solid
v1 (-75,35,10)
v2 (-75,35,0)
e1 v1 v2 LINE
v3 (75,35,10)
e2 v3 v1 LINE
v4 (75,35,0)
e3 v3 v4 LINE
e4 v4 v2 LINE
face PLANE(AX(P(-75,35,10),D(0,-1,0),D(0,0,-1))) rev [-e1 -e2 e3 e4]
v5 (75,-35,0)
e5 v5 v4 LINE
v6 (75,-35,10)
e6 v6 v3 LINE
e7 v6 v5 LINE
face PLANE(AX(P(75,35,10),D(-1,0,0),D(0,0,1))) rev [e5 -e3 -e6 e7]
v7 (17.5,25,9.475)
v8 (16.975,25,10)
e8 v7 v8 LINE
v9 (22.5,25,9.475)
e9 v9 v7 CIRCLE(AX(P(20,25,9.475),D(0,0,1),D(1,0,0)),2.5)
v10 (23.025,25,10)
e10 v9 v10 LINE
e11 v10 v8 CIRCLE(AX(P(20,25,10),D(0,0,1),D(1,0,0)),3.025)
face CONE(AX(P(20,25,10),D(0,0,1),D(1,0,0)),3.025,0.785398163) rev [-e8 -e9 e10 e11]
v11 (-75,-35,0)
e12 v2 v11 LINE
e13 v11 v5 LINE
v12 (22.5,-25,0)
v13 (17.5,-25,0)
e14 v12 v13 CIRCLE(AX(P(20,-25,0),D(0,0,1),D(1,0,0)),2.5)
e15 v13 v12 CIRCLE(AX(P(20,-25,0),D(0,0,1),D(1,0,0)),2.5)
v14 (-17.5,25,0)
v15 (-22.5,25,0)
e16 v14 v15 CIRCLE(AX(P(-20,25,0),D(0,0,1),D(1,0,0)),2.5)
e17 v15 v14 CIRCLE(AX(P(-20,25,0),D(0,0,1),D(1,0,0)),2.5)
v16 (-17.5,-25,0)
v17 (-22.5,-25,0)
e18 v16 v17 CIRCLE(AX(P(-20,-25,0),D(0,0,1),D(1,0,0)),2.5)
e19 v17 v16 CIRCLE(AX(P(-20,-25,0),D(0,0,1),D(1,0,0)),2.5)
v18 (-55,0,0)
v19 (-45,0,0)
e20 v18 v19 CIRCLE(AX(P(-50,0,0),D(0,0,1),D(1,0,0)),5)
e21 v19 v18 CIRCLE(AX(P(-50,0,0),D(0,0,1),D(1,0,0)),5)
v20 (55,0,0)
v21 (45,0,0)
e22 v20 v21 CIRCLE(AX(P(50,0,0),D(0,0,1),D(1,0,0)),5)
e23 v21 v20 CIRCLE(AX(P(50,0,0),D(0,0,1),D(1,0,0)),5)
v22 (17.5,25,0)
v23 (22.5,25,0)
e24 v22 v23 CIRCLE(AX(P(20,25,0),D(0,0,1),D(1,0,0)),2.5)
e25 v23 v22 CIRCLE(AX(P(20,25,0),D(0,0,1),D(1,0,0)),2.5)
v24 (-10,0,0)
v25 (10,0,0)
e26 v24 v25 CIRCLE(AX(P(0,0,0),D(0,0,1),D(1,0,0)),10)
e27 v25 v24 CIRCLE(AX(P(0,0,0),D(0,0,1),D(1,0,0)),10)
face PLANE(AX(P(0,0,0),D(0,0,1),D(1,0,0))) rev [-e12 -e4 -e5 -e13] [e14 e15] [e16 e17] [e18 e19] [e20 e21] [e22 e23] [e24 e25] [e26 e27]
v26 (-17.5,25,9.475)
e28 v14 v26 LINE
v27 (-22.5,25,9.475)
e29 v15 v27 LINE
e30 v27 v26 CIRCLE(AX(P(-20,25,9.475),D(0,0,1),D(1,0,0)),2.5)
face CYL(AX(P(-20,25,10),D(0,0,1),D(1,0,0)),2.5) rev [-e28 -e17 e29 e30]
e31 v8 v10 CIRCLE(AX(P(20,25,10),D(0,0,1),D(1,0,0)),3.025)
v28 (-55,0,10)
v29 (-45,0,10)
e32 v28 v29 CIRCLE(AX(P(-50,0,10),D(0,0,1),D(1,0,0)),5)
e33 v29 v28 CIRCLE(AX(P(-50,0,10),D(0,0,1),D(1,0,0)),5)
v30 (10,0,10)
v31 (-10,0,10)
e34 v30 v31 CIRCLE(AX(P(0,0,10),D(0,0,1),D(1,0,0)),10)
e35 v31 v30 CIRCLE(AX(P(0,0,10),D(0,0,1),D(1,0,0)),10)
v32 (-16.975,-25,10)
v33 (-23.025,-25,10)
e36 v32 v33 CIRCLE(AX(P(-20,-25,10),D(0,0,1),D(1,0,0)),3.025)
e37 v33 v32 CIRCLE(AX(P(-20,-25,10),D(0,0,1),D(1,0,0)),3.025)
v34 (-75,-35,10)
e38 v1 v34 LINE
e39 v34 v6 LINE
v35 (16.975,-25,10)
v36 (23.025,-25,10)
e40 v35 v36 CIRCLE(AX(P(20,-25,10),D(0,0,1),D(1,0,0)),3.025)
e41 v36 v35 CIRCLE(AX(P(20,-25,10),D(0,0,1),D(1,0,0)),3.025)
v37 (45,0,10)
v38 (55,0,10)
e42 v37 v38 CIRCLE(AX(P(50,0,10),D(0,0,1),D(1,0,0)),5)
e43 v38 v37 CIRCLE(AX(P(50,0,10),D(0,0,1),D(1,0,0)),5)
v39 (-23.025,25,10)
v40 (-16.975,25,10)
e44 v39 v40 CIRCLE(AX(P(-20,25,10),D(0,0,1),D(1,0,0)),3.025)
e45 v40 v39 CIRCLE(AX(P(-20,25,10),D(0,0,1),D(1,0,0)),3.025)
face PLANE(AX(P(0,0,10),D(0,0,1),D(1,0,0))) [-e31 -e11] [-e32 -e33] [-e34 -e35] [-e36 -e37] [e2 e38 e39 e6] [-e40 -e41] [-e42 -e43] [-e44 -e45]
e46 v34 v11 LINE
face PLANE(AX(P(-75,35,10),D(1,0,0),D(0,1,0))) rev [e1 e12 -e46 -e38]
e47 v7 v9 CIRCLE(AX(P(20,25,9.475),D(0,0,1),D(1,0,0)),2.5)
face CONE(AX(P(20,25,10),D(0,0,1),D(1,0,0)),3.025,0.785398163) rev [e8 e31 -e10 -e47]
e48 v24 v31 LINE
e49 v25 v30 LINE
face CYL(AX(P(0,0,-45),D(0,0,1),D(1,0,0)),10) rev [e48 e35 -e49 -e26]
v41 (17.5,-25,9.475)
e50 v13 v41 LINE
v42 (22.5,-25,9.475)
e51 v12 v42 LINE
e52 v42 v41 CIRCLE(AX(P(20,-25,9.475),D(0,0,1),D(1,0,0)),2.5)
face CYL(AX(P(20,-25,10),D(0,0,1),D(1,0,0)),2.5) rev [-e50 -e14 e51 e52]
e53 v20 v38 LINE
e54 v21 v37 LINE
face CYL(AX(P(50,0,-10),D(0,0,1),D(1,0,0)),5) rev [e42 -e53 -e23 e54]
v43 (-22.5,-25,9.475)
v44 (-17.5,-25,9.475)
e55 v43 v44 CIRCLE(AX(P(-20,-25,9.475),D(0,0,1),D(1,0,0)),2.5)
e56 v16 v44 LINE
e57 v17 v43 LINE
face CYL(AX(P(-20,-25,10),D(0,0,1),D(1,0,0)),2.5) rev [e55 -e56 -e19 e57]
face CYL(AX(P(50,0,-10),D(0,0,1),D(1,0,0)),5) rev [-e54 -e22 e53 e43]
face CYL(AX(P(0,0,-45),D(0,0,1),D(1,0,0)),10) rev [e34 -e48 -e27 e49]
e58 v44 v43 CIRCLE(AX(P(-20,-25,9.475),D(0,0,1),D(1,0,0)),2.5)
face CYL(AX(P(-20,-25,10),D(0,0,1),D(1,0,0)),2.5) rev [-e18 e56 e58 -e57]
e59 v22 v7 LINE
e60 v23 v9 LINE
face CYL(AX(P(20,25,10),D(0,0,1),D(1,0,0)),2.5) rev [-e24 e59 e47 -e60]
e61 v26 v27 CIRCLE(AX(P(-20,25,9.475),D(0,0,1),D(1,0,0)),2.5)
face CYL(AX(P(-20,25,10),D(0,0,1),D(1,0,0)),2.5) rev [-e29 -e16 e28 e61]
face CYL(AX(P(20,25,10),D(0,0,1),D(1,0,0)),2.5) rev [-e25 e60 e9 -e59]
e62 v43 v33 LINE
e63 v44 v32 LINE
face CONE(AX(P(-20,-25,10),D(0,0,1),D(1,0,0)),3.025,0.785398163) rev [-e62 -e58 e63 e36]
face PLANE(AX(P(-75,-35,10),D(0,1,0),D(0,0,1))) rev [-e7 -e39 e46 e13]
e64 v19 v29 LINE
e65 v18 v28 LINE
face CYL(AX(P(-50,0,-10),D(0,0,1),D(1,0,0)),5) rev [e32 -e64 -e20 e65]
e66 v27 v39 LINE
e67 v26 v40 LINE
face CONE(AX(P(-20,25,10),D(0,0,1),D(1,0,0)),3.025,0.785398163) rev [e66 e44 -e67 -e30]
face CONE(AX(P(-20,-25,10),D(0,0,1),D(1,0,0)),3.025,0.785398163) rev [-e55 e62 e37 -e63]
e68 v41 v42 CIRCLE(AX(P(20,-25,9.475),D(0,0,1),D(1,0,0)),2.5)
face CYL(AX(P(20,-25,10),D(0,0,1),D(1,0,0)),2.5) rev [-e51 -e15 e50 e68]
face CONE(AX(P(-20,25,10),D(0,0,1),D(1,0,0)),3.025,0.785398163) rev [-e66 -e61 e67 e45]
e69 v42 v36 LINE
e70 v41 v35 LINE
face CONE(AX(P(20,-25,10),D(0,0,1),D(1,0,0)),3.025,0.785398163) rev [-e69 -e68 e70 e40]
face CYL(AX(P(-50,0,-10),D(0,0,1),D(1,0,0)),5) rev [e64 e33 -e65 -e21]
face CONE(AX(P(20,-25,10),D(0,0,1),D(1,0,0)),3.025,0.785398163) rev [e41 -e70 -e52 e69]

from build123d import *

# Parameters (mm, degrees)
SKETCH_1_W                   = 150
SKETCH_1_H                   = 70
EXTRUDE_1_DEPTH              = 10
SKETCH_2_R                   = 10
CUT_EXTRUDE_1_DEPTH          = 55
SKETCH_7_R                   = 5
CUT_EXTRUDE_2_DEPTH          = 20
HOLE_WIZARD_M6_1_D           = 5
HOLE_WIZARD_M6_1_DEPTH       = 13.497848452
HOLE_WIZARD_M6_1_CSINK_D     = 6.05
HOLE_WIZARD_M6_1_CSINK_ANGLE = 90
HOLE_WIZARD_M6_1_TIP         = 1.502151548


with BuildPart() as part:
    # 草图1 → 凸台-拉伸1 (new body)
    with BuildSketch(Plane.XY):
        Rectangle(SKETCH_1_W, SKETCH_1_H)
    extrude(amount=EXTRUDE_1_DEPTH)

    # 草图2 → 切除-拉伸1 (cut)
    with BuildSketch(Plane.XY.offset(10)):
        Circle(SKETCH_2_R)
    extrude(amount=-CUT_EXTRUDE_1_DEPTH, mode=Mode.SUBTRACT)

    # 草图7 → 切除-拉伸2 (cut)
    with BuildSketch(Plane.XY.offset(10)):
        with Locations((-50, 0)):
            Circle(SKETCH_7_R)
        with Locations((50, 0)):
            Circle(SKETCH_7_R)
    extrude(amount=-CUT_EXTRUDE_2_DEPTH, mode=Mode.SUBTRACT)

    # M6 螺纹孔1
    with Locations(Plane.XY.offset(10)):
        with Locations((20, 25), (-20, 25), (-20, -25), (20, -25)):
            CounterSinkHole(HOLE_WIZARD_M6_1_D / 2, HOLE_WIZARD_M6_1_CSINK_D / 2, depth=HOLE_WIZARD_M6_1_DEPTH, counter_sink_angle=HOLE_WIZARD_M6_1_CSINK_ANGLE)
            with Locations((0, 0, -(HOLE_WIZARD_M6_1_DEPTH + HOLE_WIZARD_M6_1_TIP / 2))):  # 118° drill point
                Cone(0, HOLE_WIZARD_M6_1_D / 2, HOLE_WIZARD_M6_1_TIP, mode=Mode.SUBTRACT)


solid = part.part
